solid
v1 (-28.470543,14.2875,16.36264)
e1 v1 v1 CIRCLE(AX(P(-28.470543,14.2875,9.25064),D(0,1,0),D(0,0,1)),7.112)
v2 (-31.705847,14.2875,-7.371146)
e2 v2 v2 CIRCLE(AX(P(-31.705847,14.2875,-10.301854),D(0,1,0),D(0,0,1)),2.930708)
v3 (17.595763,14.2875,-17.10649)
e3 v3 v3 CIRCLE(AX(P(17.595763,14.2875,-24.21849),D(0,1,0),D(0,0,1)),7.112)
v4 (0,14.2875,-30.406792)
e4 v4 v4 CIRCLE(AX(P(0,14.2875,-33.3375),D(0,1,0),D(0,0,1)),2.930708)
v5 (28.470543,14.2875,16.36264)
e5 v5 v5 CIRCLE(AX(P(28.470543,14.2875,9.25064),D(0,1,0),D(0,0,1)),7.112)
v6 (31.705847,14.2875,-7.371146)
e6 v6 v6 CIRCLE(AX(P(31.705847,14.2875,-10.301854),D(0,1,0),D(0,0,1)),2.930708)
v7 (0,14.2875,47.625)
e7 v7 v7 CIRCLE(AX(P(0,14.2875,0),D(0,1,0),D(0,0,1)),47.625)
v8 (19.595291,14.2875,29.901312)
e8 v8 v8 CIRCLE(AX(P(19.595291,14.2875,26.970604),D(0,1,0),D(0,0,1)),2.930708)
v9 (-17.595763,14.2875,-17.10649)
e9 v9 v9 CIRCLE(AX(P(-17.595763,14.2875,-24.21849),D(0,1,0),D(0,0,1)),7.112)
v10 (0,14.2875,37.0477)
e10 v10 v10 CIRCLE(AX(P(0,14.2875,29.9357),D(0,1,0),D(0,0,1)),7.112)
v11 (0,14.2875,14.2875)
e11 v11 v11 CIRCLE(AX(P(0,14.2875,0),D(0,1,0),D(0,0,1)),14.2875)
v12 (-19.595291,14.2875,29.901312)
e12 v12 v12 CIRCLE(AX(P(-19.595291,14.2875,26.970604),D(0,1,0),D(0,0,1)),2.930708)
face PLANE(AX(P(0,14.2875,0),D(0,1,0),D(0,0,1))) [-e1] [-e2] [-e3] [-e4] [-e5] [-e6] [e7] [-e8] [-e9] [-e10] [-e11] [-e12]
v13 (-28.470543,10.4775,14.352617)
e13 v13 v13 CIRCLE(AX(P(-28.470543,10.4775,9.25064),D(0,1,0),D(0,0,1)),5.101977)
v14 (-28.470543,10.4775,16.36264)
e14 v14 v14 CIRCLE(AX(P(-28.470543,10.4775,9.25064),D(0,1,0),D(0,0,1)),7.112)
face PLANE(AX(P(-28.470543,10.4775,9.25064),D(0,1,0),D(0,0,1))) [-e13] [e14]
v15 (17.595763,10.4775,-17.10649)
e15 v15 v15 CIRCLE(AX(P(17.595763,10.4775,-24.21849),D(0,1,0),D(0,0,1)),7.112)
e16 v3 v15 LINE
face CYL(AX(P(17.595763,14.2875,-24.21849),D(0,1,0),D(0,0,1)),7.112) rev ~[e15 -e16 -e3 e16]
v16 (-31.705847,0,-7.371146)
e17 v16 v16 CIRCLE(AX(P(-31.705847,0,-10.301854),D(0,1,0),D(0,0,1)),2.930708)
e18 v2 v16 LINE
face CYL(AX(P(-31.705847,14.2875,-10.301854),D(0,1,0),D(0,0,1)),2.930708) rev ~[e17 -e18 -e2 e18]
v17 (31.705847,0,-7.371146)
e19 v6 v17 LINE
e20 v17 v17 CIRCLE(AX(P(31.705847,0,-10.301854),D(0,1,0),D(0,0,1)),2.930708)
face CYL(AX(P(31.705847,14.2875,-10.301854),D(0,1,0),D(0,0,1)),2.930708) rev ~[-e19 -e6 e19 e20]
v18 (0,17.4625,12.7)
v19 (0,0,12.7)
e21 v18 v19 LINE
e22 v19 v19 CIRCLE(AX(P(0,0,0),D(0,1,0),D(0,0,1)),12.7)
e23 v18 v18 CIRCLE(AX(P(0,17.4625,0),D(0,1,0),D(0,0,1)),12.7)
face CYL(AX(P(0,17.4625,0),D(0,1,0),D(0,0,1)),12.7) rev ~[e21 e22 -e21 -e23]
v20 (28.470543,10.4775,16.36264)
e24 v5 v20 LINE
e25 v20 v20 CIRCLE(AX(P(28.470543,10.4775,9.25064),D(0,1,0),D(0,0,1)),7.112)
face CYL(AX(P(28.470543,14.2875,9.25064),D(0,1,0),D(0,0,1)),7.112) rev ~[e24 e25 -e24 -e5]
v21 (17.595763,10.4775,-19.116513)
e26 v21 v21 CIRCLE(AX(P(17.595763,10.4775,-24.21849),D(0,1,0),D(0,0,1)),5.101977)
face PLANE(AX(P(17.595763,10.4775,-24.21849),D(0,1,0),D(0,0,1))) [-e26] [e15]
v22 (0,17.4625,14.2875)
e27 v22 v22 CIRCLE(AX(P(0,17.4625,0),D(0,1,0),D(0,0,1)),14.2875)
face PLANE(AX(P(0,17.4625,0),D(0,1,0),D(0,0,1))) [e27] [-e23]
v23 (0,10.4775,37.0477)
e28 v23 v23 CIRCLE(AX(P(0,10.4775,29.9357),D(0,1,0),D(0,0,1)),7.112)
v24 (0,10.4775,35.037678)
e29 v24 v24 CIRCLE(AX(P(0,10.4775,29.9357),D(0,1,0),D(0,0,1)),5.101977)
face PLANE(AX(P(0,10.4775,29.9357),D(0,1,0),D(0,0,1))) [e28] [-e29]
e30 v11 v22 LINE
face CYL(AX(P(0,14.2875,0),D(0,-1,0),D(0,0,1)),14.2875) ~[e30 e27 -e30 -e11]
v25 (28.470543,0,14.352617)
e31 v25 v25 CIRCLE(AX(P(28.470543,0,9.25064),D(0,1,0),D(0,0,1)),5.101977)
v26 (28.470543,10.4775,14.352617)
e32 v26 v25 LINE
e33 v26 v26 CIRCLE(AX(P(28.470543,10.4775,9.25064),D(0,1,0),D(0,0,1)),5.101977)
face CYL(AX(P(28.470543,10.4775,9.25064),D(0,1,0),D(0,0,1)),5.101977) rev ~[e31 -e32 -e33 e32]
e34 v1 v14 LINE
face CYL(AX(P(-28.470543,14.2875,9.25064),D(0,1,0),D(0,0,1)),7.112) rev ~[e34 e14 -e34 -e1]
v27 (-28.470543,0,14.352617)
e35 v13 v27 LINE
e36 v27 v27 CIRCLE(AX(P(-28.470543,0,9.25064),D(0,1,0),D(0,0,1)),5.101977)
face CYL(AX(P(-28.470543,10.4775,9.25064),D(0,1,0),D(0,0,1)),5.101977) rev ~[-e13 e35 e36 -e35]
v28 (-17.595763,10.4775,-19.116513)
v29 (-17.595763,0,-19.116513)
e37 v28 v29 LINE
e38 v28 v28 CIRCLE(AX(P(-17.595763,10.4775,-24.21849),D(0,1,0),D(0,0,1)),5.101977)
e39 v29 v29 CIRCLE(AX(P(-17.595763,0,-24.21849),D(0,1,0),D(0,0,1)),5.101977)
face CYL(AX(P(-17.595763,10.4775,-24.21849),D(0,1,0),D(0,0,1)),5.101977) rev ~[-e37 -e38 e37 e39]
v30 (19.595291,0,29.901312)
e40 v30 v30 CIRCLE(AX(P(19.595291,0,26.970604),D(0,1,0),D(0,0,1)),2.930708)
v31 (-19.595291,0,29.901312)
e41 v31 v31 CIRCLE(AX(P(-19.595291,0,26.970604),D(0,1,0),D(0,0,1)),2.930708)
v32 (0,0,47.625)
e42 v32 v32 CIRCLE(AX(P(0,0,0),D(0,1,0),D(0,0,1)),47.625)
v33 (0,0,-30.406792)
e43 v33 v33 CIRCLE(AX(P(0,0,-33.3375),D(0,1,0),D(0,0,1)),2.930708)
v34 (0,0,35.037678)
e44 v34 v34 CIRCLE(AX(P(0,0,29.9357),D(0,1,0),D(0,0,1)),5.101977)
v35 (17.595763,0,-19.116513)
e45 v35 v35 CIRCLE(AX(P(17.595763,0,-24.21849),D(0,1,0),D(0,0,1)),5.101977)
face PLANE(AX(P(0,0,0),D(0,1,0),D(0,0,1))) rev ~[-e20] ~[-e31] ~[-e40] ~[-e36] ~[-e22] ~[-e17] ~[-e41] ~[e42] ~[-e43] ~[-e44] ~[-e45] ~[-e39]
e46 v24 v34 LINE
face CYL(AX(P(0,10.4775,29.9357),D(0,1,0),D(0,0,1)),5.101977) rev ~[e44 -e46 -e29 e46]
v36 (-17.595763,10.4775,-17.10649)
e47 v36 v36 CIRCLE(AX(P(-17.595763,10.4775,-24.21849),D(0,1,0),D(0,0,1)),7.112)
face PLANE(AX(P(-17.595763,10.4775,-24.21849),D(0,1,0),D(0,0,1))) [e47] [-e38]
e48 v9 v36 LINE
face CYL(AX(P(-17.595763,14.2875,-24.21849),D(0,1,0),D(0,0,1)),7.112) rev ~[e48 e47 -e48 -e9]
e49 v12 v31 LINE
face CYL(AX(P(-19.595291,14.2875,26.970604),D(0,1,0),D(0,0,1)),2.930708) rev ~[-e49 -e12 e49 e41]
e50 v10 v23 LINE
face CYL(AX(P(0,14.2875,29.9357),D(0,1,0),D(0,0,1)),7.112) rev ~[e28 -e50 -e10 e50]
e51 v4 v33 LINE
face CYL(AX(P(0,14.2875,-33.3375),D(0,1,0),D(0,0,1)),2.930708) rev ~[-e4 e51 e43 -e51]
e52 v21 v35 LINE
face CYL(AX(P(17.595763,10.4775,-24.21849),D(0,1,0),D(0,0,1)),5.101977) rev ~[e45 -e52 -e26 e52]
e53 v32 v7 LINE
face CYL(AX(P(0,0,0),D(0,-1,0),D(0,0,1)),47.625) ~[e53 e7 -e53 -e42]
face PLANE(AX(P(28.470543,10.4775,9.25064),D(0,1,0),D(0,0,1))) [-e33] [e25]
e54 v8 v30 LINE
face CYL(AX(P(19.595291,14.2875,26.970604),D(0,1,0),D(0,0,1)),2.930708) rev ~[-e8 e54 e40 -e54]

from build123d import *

# Parameters (mm, degrees)
FLANGE_DISC_SKETCH_R              = 47.625
FLANGE_DISC_3_75_DEPTH            = 14.2875
TAPPED_HOLES_SKETCH_R             = 2.930707565
TAPPED_HOLES_5X_ON_BC_2_625_DEPTH = 14.2875
HUB_BOSS_SKETCH_R                 = 14.2875
HUB_BOSS_1_125_DEPTH              = 3.175
CENTER_BORE_SKETCH_R              = 12.7
CENTER_BORE_1_0_DEPTH             = 34.925
COUNTERBORES_SKETCH_R             = 7.112
COUNTERBORES_5X_0_56_DEPTH        = 3.81
BOLT_HOLES_SKETCH_R               = 5.10197716
COUNTERBORED_BOLT_HOLES_5X_DEPTH  = 16.51


with BuildPart() as part:
    # Flange Disc Sketch → Flange Disc Ø3.75 (new body)
    with BuildSketch(Plane(origin=(0, 0, 0), x_dir=(1, 0, 0), z_dir=(0, 1, 0))):
        with Locations(Location((0, 0, 0), (0, 0, 270))):
            Circle(FLANGE_DISC_SKETCH_R)
    extrude(amount=FLANGE_DISC_3_75_DEPTH)

    # Tapped Holes Sketch → Tapped Holes 5x on BC Ø2.625 (cut)
    with BuildSketch(Plane(origin=(0, 14.2875, 0), x_dir=(1, 0, 0), z_dir=(0, 1, 0))):
        with Locations(Location((0, 33.3375, 0), (0, 0, 270))):
            Circle(TAPPED_HOLES_SKETCH_R)
        with Locations(Location((31.705846612, 10.30185405, 0), (0, 0, 270))):
            Circle(TAPPED_HOLES_SKETCH_R)
        with Locations(Location((19.595290848, -26.97060405, 0), (0, 0, 270))):
            Circle(TAPPED_HOLES_SKETCH_R)
        with Locations(Location((-19.595290848, -26.97060405, 0), (0, 0, 270))):
            Circle(TAPPED_HOLES_SKETCH_R)
        with Locations(Location((-31.705846612, 10.30185405, 0), (0, 0, 270))):
            Circle(TAPPED_HOLES_SKETCH_R)
    extrude(amount=-TAPPED_HOLES_5X_ON_BC_2_625_DEPTH, mode=Mode.SUBTRACT)

    # Hub Boss Sketch → Hub Boss Ø1.125 (add)
    with BuildSketch(Plane(origin=(0, 14.2875, 0), x_dir=(1, 0, 0), z_dir=(0, 1, 0))):
        with Locations(Location((0, 0, 0), (0, 0, 270))):
            Circle(HUB_BOSS_SKETCH_R)
    extrude(amount=HUB_BOSS_1_125_DEPTH)

    # Center Bore Sketch → Center Bore Ø1.0 (cut)
    with BuildSketch(Plane(origin=(0, 17.4625, 0), x_dir=(1, 0, 0), z_dir=(0, 1, 0))):
        with Locations(Location((0, 0, 0), (0, 0, 270))):
            Circle(CENTER_BORE_SKETCH_R)
    extrude(amount=-CENTER_BORE_1_0_DEPTH, mode=Mode.SUBTRACT)

    # Counterbores Sketch → Counterbores 5xØ0.56 (cut)
    with BuildSketch(Plane(origin=(0, 14.2875, 0), x_dir=(1, 0, 0), z_dir=(0, 1, 0))):
        with Locations(Location((0, -29.935700362, 0), (0, 0, 270))):
            Circle(COUNTERBORES_SKETCH_R)
        with Locations(Location((-28.470542899, -9.25064015, 0), (0, 0, 270))):
            Circle(COUNTERBORES_SKETCH_R)
        with Locations(Location((-17.59576319, 24.218490331, 0), (0, 0, 270))):
            Circle(COUNTERBORES_SKETCH_R)
        with Locations(Location((17.59576319, 24.218490331, 0), (0, 0, 270))):
            Circle(COUNTERBORES_SKETCH_R)
        with Locations(Location((28.470542899, -9.25064015, 0), (0, 0, 270))):
            Circle(COUNTERBORES_SKETCH_R)
    extrude(amount=-COUNTERBORES_5X_0_56_DEPTH, mode=Mode.SUBTRACT)

    # Bolt Holes Sketch → Counterbored Bolt Holes 5x (cut)
    with BuildSketch(Plane(origin=(0, 10.4775, 0), x_dir=(1, 0, 0), z_dir=(0, 1, 0))):
        with Locations(Location((0, -29.935700362, 0), (0, 0, 270))):
            Circle(BOLT_HOLES_SKETCH_R)
        with Locations(Location((-28.470542899, -9.25064015, 0), (0, 0, 270))):
            Circle(BOLT_HOLES_SKETCH_R)
        with Locations(Location((-17.59576319, 24.218490331, 0), (0, 0, 270))):
            Circle(BOLT_HOLES_SKETCH_R)
        with Locations(Location((17.59576319, 24.218490331, 0), (0, 0, 270))):
            Circle(BOLT_HOLES_SKETCH_R)
        with Locations(Location((28.470542899, -9.25064015, 0), (0, 0, 270))):
            Circle(BOLT_HOLES_SKETCH_R)
    extrude(amount=-COUNTERBORED_BOLT_HOLES_5X_DEPTH, mode=Mode.SUBTRACT)


solid = part.part
